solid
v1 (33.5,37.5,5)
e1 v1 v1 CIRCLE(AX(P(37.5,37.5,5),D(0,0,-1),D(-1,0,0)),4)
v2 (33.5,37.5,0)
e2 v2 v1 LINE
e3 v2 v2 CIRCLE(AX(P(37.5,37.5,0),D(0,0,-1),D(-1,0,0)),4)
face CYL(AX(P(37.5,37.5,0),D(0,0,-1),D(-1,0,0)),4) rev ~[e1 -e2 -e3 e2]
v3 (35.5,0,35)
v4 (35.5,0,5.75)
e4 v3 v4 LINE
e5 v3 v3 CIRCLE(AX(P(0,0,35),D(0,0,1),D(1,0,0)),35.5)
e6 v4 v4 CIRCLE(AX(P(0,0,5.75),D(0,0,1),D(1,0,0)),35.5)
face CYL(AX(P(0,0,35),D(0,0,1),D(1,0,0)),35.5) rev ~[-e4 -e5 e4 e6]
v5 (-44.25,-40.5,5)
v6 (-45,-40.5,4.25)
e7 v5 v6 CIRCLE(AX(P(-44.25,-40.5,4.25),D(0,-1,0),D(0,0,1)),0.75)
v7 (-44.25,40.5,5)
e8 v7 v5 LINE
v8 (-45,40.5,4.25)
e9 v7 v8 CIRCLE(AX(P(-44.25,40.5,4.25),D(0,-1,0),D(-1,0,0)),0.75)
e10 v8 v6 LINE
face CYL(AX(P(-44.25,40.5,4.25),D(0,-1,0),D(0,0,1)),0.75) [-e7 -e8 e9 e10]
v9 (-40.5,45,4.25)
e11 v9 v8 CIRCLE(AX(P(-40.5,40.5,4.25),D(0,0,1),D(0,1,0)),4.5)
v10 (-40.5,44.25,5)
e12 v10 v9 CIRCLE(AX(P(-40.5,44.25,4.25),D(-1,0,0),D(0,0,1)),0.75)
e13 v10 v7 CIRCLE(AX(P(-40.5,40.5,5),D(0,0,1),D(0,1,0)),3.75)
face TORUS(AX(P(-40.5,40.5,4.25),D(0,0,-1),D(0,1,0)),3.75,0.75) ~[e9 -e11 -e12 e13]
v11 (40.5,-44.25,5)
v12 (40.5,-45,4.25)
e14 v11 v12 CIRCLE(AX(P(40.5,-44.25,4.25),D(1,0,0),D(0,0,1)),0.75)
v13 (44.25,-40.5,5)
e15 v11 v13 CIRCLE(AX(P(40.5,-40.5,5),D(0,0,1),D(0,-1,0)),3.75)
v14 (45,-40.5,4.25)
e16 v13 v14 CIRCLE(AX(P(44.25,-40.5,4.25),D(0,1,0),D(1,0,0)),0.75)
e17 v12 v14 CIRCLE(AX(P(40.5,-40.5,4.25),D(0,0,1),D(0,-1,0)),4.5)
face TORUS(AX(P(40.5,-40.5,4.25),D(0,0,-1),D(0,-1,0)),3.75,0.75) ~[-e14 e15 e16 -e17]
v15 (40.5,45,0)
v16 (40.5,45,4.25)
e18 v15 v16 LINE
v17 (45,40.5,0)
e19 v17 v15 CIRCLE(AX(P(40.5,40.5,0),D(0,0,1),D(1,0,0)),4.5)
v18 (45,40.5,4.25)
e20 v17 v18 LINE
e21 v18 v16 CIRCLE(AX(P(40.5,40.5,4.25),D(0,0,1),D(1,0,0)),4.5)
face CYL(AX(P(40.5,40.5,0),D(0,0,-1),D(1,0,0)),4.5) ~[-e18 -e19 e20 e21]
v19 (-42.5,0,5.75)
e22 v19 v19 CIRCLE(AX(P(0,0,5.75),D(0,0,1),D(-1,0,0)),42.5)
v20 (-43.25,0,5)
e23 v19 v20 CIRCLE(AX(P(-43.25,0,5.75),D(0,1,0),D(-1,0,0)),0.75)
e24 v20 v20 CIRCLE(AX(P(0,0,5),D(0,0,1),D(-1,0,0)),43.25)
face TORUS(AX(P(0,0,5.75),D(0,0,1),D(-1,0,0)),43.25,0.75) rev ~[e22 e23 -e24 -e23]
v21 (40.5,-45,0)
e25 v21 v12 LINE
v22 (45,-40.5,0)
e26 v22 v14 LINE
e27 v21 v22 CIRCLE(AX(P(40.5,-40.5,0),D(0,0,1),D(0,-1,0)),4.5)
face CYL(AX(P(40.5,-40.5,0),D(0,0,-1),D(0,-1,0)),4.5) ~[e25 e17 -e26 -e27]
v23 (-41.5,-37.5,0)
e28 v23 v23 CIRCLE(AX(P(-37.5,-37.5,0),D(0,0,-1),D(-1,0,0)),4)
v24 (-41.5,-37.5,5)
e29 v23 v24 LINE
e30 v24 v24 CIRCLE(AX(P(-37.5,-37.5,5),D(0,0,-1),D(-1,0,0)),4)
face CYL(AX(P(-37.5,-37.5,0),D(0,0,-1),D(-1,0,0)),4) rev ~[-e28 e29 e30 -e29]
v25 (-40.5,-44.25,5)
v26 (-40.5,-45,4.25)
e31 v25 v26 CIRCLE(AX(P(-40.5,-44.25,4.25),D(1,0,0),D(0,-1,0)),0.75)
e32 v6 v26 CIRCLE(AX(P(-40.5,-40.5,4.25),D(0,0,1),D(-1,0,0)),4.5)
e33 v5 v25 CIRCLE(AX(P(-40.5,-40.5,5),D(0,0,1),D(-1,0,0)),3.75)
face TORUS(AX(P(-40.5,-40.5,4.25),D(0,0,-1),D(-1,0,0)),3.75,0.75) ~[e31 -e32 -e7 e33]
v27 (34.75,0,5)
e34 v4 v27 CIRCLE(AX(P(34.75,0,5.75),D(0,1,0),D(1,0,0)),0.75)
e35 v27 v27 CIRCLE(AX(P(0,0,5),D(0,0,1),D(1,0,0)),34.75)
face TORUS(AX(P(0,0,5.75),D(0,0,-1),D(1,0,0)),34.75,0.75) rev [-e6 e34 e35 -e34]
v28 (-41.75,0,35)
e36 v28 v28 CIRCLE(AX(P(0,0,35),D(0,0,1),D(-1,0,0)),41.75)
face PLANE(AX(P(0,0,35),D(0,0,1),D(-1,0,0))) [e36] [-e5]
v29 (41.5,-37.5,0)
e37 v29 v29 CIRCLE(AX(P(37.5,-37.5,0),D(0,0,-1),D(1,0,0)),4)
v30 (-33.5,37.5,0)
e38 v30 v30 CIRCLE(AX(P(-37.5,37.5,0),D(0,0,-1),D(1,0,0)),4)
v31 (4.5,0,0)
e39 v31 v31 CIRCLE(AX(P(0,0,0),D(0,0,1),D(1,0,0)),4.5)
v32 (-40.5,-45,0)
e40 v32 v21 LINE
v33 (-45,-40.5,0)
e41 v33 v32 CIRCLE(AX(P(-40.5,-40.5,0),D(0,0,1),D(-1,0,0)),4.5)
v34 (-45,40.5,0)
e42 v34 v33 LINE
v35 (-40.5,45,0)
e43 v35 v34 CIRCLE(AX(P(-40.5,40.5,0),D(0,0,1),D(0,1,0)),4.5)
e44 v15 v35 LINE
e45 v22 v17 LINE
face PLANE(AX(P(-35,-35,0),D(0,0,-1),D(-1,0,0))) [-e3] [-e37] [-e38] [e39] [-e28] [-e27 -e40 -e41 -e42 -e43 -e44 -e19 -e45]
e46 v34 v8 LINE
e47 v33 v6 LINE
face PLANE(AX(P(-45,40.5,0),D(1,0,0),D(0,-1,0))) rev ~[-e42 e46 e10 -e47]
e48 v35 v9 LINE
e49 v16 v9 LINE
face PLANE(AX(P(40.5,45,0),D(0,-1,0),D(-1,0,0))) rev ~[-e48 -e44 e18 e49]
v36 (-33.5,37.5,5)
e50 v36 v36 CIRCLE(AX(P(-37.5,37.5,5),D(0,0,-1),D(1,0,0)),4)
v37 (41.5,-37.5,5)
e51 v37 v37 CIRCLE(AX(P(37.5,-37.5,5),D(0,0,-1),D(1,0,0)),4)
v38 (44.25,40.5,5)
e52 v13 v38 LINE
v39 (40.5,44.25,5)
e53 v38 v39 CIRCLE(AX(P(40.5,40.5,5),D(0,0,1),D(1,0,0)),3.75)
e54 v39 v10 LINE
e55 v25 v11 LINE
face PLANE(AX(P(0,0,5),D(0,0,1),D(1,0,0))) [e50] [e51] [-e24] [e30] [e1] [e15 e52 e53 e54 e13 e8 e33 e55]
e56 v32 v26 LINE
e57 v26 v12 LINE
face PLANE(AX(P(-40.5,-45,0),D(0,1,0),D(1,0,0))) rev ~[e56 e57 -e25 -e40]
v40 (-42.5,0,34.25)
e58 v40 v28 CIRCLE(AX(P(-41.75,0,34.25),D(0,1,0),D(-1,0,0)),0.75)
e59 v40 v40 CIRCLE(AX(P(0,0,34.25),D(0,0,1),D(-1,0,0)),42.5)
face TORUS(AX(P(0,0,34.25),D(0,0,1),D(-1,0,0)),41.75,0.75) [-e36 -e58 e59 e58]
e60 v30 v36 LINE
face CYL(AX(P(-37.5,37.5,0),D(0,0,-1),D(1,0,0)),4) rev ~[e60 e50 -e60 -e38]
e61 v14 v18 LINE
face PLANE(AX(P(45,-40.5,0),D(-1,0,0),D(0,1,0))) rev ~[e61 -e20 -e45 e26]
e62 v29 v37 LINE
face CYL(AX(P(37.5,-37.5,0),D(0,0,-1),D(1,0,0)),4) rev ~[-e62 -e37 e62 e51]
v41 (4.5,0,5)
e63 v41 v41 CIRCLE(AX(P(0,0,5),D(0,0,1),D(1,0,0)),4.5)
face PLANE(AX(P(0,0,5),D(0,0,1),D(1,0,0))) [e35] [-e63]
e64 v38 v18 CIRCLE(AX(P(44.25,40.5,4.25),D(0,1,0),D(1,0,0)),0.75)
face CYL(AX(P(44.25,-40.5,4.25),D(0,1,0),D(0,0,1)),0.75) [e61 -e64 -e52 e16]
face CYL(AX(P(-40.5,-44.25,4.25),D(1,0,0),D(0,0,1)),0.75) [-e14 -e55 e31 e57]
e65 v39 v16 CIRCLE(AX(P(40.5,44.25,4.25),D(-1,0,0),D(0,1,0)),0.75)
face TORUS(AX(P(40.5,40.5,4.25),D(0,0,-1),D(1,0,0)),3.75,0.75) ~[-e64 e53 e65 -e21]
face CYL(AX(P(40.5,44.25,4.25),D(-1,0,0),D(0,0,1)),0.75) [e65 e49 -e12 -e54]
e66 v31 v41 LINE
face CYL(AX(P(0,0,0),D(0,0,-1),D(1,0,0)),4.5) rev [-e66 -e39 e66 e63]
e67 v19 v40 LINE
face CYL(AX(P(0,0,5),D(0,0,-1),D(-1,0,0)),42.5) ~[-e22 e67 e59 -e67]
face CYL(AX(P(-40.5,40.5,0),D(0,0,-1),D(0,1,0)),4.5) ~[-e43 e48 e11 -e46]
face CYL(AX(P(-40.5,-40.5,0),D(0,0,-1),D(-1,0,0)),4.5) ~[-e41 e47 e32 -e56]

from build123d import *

# Parameters (mm, degrees)
SKETCH1_R           = 9
SKETCH1_R_2         = 4.5
BOSS_EXTRUDE1_DEPTH = 10
SKETCH2_R           = 85
BOSS_EXTRUDE2_DEPTH = 60
SKETCH3_R           = 71
CUT_EXTRUDE1_DEPTH  = 60
FILLET1_R           = 1.5
SCALE1_SCALE        = 0.5
SKETCH_1_R          = 2.25
EXTRUDE_1_DEPTH     = 5
SKETCH_2_R          = 4
CUT_EXTRUDE_1_DEPTH = 10


with BuildPart() as part:
    # Sketch1 → Boss-Extrude1 (new body)
    with BuildSketch(Plane.XY):
        with BuildLine():
            Line((-81, -90), (81, -90))
            ThreePointArc((81, -90), (87.363961031, -87.363961031), (90, -81))
            Line((90, -81), (90, 81))
            ThreePointArc((90, 81), (87.363961031, 87.363961031), (81, 90))
            Line((81, 90), (-81, 90))
            ThreePointArc((-81, 90), (-87.363961031, 87.363961031), (-90, 81))
            Line((-90, 81), (-90, -81))
            ThreePointArc((-90, -81), (-87.363961031, -87.363961031), (-81, -90))
        make_face()
        Circle(SKETCH1_R, mode=Mode.SUBTRACT)
        with Locations((70, 70)):
            Circle(SKETCH1_R_2, mode=Mode.SUBTRACT)
        with Locations(Location((-70, 70, 0), (0, 0, 180))):
            Circle(SKETCH1_R_2, mode=Mode.SUBTRACT)
        with Locations(Location((70, -70, 0), (0, 0, 180))):
            Circle(SKETCH1_R_2, mode=Mode.SUBTRACT)
        with Locations((-70, -70)):
            Circle(SKETCH1_R_2, mode=Mode.SUBTRACT)
    extrude(amount=BOSS_EXTRUDE1_DEPTH)

    # Sketch2 → Boss-Extrude2 (add)
    with BuildSketch(Plane.XY.offset(10)):
        with Locations(Location((0, 0, 0), (0, 0, 180))):
            Circle(SKETCH2_R)
    extrude(amount=BOSS_EXTRUDE2_DEPTH)

    # Sketch3 → Cut-Extrude1 (cut)
    with BuildSketch(Plane.XY.offset(70)):
        Circle(SKETCH3_R)
    extrude(amount=-CUT_EXTRUDE1_DEPTH, mode=Mode.SUBTRACT)

    # Fillet1
    fillet1_edges = [part.edges().sort_by_distance(p)[0] for p in [
        (87.363961031, 87.363961031, 10),
        (0, 90, 10),
        (-87.363961031, 87.363961031, 10),
        (-90, 0, 10),
        (-87.363961031, -87.363961031, 10),
        (0, -90, 10),
        (87.363961031, -87.363961031, 10),
        (85, 0, 10),
        (85, 0, 70),
        (-71, 0, 10),
        (90, 0, 10),
    ]]
    fillet(fillet1_edges, radius=FILLET1_R)


with BuildPart() as part_1:
    # Scale1: scaled about (0, 0, 0)
    add(part.part.scale(SCALE1_SCALE))

    # 草图1 → 凸台-拉伸1 (add)
    with BuildSketch(Plane(origin=(0, 0, 0), x_dir=(-1, 0, 0), z_dir=(0, 0, -1))):
        with Locations((35, -35)):
            Circle(SKETCH_1_R)
        with Locations((-35, -35)):
            Circle(SKETCH_1_R)
        with Locations((-35, 35)):
            Circle(SKETCH_1_R)
        with Locations((35, 35)):
            Circle(SKETCH_1_R)
    extrude(amount=-EXTRUDE_1_DEPTH)

    # 草图2 → 切除-拉伸1 (cut)
    with BuildSketch(Plane(origin=(0, 0, 0), x_dir=(-1, 0, 0), z_dir=(0, 0, -1))):
        with Locations((-37.5, 37.5)):
            Circle(SKETCH_2_R)
        with Locations(Location((-37.5, -37.5, 0), (0, 0, 180))):
            Circle(SKETCH_2_R)
        with Locations(Location((37.5, 37.5, 0), (0, 0, 180))):
            Circle(SKETCH_2_R)
        with Locations((37.5, -37.5)):
            Circle(SKETCH_2_R)
    extrude(amount=-CUT_EXTRUDE_1_DEPTH, mode=Mode.SUBTRACT)


solid = part_1.part
